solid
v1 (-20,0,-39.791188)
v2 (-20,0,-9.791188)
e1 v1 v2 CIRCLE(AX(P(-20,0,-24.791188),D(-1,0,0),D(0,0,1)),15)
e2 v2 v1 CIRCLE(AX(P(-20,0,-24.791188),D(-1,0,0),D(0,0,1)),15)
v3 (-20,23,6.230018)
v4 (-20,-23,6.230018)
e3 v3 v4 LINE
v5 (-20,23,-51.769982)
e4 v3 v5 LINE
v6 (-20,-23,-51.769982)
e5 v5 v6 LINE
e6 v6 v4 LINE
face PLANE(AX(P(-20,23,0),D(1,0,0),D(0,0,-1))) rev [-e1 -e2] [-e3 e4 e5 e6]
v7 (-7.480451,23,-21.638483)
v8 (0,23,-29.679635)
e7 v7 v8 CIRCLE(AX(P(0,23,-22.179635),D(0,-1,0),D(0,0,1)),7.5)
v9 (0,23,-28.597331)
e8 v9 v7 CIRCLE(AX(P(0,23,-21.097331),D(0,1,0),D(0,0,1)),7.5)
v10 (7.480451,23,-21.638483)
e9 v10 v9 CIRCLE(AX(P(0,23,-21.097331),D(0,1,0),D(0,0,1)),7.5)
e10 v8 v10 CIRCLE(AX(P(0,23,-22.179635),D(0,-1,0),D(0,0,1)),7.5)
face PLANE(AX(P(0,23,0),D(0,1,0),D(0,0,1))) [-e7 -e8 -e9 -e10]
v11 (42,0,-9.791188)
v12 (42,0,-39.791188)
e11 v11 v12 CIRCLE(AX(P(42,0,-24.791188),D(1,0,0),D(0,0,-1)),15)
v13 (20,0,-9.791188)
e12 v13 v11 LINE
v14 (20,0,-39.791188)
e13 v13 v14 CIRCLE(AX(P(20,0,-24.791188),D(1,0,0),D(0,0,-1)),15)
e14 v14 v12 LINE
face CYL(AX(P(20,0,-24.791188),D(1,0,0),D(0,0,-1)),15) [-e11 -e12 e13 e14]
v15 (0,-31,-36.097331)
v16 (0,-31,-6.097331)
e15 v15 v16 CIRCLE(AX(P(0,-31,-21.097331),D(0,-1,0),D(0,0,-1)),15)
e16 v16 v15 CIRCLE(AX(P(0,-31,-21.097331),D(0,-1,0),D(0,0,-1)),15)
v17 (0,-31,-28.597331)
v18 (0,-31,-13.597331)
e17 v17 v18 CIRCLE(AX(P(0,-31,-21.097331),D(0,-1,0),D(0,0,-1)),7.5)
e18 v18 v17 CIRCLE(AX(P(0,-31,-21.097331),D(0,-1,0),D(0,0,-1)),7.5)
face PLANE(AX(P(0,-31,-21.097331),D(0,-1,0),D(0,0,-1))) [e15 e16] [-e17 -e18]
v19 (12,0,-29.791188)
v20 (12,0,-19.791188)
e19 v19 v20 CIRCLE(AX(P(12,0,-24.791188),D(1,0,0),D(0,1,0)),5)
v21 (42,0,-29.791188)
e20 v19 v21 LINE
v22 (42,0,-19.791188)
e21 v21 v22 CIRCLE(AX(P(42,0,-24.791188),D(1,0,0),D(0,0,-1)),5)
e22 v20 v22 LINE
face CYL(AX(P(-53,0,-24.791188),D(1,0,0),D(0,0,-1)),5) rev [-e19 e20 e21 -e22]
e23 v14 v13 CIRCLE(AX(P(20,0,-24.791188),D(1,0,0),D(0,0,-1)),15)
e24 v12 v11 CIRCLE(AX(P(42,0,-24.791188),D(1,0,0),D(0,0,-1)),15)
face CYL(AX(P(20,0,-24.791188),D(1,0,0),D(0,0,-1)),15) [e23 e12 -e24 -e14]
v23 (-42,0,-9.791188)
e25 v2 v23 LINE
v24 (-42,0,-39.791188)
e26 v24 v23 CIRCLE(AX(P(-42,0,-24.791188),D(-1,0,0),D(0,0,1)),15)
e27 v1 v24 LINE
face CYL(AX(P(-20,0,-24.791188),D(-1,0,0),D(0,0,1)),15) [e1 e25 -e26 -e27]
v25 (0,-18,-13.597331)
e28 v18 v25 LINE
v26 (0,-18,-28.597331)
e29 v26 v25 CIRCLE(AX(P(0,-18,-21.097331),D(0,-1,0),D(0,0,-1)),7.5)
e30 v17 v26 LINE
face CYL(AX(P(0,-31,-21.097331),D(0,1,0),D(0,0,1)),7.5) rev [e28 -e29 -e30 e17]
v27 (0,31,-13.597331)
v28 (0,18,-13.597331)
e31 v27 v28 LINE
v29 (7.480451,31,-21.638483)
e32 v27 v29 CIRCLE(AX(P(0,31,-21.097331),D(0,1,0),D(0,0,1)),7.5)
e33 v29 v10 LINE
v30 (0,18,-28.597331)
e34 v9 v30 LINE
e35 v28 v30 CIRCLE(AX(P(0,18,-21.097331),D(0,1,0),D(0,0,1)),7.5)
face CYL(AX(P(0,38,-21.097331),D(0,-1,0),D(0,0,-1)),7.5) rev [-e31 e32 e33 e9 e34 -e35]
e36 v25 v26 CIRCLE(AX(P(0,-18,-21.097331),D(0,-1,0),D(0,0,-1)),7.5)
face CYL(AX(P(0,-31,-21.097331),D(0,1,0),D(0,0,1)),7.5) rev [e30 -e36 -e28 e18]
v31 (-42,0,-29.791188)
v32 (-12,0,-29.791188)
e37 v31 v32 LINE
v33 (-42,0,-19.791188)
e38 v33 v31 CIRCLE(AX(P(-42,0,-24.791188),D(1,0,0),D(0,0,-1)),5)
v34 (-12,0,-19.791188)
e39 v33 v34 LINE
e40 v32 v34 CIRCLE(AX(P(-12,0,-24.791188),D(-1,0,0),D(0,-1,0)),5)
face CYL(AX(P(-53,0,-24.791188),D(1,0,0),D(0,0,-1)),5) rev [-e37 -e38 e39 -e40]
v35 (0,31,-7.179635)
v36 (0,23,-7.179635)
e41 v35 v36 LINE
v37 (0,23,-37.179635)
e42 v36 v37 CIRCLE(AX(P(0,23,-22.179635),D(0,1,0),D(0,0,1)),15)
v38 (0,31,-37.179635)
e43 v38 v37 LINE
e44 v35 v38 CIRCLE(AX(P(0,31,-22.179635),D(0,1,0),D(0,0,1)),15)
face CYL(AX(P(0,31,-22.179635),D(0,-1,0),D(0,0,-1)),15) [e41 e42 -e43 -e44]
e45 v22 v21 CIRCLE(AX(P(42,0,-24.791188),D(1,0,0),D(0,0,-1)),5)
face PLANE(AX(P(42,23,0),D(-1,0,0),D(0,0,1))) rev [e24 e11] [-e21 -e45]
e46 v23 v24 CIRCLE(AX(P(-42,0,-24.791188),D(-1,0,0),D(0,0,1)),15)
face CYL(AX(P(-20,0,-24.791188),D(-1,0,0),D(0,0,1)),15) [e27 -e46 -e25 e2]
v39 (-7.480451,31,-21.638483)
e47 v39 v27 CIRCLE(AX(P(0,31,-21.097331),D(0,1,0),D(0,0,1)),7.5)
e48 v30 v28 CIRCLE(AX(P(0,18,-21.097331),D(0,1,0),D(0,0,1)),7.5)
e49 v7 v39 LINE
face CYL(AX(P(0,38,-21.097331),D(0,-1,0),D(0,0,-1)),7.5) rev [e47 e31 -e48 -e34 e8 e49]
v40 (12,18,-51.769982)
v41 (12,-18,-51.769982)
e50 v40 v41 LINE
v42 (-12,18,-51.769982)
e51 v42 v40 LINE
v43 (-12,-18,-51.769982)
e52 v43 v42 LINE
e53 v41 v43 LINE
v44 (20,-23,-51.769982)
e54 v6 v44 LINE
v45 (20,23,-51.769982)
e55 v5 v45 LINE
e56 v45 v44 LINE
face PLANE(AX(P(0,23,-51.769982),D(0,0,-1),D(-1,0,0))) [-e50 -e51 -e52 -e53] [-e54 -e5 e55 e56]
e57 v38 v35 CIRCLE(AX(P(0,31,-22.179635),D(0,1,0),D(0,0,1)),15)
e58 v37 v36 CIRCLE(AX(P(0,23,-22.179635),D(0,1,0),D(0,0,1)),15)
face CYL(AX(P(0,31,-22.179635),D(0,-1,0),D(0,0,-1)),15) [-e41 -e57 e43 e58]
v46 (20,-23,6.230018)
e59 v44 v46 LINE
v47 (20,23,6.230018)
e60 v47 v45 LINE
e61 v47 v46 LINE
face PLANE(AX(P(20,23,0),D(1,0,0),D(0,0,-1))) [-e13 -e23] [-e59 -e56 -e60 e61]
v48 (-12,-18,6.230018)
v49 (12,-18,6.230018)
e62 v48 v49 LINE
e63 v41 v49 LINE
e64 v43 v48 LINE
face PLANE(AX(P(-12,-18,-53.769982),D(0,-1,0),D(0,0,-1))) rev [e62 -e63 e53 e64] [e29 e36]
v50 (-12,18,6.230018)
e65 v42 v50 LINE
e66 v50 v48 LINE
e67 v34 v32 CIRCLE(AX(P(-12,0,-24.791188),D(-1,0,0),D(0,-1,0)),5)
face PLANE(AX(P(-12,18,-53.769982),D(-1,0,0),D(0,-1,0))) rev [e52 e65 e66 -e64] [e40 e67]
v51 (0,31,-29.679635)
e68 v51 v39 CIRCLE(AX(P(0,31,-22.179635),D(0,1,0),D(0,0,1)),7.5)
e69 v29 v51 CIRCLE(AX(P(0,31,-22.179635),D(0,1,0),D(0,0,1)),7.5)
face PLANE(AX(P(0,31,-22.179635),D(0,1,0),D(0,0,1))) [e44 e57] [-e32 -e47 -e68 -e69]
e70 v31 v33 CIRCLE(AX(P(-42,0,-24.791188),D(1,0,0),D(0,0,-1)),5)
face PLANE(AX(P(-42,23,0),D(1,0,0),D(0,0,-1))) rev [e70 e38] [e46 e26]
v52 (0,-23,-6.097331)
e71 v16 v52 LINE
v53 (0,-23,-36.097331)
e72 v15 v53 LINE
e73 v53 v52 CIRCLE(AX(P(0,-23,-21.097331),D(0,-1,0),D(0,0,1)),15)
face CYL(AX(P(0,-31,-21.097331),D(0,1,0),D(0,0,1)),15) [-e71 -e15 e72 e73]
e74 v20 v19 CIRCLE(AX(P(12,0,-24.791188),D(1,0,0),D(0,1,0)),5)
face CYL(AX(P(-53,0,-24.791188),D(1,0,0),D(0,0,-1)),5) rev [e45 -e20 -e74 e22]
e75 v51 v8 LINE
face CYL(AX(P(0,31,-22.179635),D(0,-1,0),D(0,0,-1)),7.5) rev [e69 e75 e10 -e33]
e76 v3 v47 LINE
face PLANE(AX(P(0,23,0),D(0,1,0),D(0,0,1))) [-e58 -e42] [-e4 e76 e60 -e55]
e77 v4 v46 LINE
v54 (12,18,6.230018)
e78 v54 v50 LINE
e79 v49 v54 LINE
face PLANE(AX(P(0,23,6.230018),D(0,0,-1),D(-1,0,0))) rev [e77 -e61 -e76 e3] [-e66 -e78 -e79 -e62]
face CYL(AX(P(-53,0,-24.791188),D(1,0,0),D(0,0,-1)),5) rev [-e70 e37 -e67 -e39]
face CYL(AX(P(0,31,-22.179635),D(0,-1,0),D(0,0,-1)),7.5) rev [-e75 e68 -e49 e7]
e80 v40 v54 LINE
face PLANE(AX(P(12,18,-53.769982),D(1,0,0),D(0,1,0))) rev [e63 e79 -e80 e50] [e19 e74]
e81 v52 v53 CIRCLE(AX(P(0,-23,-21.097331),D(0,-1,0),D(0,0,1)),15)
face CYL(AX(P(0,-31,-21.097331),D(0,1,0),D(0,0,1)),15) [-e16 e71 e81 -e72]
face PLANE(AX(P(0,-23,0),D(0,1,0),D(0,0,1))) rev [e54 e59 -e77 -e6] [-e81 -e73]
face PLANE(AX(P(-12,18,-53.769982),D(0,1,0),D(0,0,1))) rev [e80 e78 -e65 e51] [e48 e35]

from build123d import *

# Parameters (mm, degrees)
VALVE_BODY_PROFILE_SKETCH_W  = 84
VALVE_BODY_PROFILE_SKETCH_H  = 46
VALVE_BODY_BLOCK_DEPTH       = 23
TOP_PORT_BOSS_SKETCH_R       = 15
TOP_PORT_BOSS_SKETCH_R_2     = 7.5
TOP_PORT_BOSS_30_DEPTH       = 8
BODY_WINDOW_SKETCH_W         = 24
BODY_WINDOW_SKETCH_H         = 36
BODY_WINDOW_CUT_24X36_DEPTH  = 60
SIDE_PORT_SKETCH_R           = 5
SIDE_PORT_THROUGH_BORE_DEPTH = 95
SKETCH4_3_R                  = 15
SKETCH4_3_R_2                = 5
SIDE_PORT_CUT_DEPTH          = 22
REAR_START                   = -22
REAR_PORT_SKETCH_W           = 46
REAR_PORT_SKETCH_H           = 46
REAR_PORT_SKETCH_R           = 15
REAR_PORT_CUT_DEPTH          = 22
FRONT_PORT_BOSS_SKETCH_R     = 15
FRONT_PORT_BOSS_SKETCH_R_2   = 7.5
FRONT_PORT_BOSS_30_DEPTH     = 8
FRONT_START                  = -61
SKETCH6_3_R                  = 7.5
FRONT_PORT_BORE_DEPTH        = 61


with BuildPart() as part:
    # Valve Body Profile Sketch → Valve Body Block (new, symmetric)
    with BuildSketch(Plane(origin=(0, 0, 0), x_dir=(1, 0, 0), z_dir=(0, 1, 0))):
        with Locations((0, 23)):
            Rectangle(VALVE_BODY_PROFILE_SKETCH_W, VALVE_BODY_PROFILE_SKETCH_H)
        Polygon((-20, 51.769982338), (20, 51.769982338), (20, 22.392939221), (20, -6.230017662), (-20, -6.230017662), (-20, 23), align=None)
    extrude(amount=VALVE_BODY_BLOCK_DEPTH, both=True)

    # Top Port Boss Sketch → Top Port Boss _30 (add)
    with BuildSketch(Plane(origin=(0, 23, 0), x_dir=(1, 0, 0), z_dir=(0, 1, 0))):
        with Locations(Location((0, 22.179634707, 0), (0, 0, 270))):
            Circle(TOP_PORT_BOSS_SKETCH_R)
        with Locations(Location((0, 22.179634707, 0), (0, 0, 270))):
            Circle(TOP_PORT_BOSS_SKETCH_R_2, mode=Mode.SUBTRACT)
    extrude(amount=TOP_PORT_BOSS_30_DEPTH)

    # Body Window Sketch → Body Window Cut 24x36 (cut)
    with BuildSketch(Plane.XY.offset(6.230017662)):
        Rectangle(BODY_WINDOW_SKETCH_W, BODY_WINDOW_SKETCH_H)
    extrude(amount=-BODY_WINDOW_CUT_24X36_DEPTH, mode=Mode.SUBTRACT)

    # Side Port Sketch → Side Port Through Bore (cut)
    with BuildSketch(Plane(origin=(42, 0, 0), x_dir=(0, 0, -1), z_dir=(1, 0, 0))):
        with Locations((24.791188033, 0)):
            Circle(SIDE_PORT_SKETCH_R)
    extrude(amount=-SIDE_PORT_THROUGH_BORE_DEPTH, mode=Mode.SUBTRACT)

    # Sketch4_3 → Side Port Cut (cut)
    # profile 1 of 2: a face of its own
    with BuildSketch(Plane(origin=(42, 0, 0), x_dir=(0, 0, -1), z_dir=(1, 0, 0))):
        Polygon((23.784682636, 23), (46, 23), (46, -23), (0, -23), (0, 23), align=None)
        with Locations((24.791188033, 0)):
            Circle(SKETCH4_3_R, mode=Mode.SUBTRACT)
    # profile 2 of 2: a face of its own
    with BuildSketch(Plane(origin=(42, 0, 0), x_dir=(0, 0, -1), z_dir=(1, 0, 0))):
        with Locations((24.791188033, 0)):
            Circle(SKETCH4_3_R_2)
    extrude(amount=-SIDE_PORT_CUT_DEPTH, mode=Mode.SUBTRACT)

    # Rear Port Sketch → Rear Port Cut (cut)
    with BuildSketch(Plane.ZY.offset(42).offset(REAR_START)):
        with Locations((-23, 0)):
            Rectangle(REAR_PORT_SKETCH_W, REAR_PORT_SKETCH_H)
        with Locations(Location((-24.791188033, 0, 0), (0, 0, 180))):
            Circle(REAR_PORT_SKETCH_R, mode=Mode.SUBTRACT)
    extrude(amount=REAR_PORT_CUT_DEPTH, mode=Mode.SUBTRACT)

    # Front Port Boss Sketch → Front Port Boss _30 (add)
    with BuildSketch(Plane.XZ.offset(23)):
        with Locations(Location((0, -21.097330719, 0), (0, 0, 90))):
            Circle(FRONT_PORT_BOSS_SKETCH_R)
        with Locations(Location((0, -21.097330719, 0), (0, 0, 270))):
            Circle(FRONT_PORT_BOSS_SKETCH_R_2, mode=Mode.SUBTRACT)
    extrude(amount=FRONT_PORT_BOSS_30_DEPTH)

    # Sketch6_3 → Front Port Bore (cut)
    with BuildSketch(Plane.XZ.offset(23).offset(FRONT_START)):
        with Locations(Location((0, -21.097330719, 0), (0, 0, 270))):
            Circle(SKETCH6_3_R)
    extrude(amount=FRONT_PORT_BORE_DEPTH, mode=Mode.SUBTRACT)


solid = part.part
